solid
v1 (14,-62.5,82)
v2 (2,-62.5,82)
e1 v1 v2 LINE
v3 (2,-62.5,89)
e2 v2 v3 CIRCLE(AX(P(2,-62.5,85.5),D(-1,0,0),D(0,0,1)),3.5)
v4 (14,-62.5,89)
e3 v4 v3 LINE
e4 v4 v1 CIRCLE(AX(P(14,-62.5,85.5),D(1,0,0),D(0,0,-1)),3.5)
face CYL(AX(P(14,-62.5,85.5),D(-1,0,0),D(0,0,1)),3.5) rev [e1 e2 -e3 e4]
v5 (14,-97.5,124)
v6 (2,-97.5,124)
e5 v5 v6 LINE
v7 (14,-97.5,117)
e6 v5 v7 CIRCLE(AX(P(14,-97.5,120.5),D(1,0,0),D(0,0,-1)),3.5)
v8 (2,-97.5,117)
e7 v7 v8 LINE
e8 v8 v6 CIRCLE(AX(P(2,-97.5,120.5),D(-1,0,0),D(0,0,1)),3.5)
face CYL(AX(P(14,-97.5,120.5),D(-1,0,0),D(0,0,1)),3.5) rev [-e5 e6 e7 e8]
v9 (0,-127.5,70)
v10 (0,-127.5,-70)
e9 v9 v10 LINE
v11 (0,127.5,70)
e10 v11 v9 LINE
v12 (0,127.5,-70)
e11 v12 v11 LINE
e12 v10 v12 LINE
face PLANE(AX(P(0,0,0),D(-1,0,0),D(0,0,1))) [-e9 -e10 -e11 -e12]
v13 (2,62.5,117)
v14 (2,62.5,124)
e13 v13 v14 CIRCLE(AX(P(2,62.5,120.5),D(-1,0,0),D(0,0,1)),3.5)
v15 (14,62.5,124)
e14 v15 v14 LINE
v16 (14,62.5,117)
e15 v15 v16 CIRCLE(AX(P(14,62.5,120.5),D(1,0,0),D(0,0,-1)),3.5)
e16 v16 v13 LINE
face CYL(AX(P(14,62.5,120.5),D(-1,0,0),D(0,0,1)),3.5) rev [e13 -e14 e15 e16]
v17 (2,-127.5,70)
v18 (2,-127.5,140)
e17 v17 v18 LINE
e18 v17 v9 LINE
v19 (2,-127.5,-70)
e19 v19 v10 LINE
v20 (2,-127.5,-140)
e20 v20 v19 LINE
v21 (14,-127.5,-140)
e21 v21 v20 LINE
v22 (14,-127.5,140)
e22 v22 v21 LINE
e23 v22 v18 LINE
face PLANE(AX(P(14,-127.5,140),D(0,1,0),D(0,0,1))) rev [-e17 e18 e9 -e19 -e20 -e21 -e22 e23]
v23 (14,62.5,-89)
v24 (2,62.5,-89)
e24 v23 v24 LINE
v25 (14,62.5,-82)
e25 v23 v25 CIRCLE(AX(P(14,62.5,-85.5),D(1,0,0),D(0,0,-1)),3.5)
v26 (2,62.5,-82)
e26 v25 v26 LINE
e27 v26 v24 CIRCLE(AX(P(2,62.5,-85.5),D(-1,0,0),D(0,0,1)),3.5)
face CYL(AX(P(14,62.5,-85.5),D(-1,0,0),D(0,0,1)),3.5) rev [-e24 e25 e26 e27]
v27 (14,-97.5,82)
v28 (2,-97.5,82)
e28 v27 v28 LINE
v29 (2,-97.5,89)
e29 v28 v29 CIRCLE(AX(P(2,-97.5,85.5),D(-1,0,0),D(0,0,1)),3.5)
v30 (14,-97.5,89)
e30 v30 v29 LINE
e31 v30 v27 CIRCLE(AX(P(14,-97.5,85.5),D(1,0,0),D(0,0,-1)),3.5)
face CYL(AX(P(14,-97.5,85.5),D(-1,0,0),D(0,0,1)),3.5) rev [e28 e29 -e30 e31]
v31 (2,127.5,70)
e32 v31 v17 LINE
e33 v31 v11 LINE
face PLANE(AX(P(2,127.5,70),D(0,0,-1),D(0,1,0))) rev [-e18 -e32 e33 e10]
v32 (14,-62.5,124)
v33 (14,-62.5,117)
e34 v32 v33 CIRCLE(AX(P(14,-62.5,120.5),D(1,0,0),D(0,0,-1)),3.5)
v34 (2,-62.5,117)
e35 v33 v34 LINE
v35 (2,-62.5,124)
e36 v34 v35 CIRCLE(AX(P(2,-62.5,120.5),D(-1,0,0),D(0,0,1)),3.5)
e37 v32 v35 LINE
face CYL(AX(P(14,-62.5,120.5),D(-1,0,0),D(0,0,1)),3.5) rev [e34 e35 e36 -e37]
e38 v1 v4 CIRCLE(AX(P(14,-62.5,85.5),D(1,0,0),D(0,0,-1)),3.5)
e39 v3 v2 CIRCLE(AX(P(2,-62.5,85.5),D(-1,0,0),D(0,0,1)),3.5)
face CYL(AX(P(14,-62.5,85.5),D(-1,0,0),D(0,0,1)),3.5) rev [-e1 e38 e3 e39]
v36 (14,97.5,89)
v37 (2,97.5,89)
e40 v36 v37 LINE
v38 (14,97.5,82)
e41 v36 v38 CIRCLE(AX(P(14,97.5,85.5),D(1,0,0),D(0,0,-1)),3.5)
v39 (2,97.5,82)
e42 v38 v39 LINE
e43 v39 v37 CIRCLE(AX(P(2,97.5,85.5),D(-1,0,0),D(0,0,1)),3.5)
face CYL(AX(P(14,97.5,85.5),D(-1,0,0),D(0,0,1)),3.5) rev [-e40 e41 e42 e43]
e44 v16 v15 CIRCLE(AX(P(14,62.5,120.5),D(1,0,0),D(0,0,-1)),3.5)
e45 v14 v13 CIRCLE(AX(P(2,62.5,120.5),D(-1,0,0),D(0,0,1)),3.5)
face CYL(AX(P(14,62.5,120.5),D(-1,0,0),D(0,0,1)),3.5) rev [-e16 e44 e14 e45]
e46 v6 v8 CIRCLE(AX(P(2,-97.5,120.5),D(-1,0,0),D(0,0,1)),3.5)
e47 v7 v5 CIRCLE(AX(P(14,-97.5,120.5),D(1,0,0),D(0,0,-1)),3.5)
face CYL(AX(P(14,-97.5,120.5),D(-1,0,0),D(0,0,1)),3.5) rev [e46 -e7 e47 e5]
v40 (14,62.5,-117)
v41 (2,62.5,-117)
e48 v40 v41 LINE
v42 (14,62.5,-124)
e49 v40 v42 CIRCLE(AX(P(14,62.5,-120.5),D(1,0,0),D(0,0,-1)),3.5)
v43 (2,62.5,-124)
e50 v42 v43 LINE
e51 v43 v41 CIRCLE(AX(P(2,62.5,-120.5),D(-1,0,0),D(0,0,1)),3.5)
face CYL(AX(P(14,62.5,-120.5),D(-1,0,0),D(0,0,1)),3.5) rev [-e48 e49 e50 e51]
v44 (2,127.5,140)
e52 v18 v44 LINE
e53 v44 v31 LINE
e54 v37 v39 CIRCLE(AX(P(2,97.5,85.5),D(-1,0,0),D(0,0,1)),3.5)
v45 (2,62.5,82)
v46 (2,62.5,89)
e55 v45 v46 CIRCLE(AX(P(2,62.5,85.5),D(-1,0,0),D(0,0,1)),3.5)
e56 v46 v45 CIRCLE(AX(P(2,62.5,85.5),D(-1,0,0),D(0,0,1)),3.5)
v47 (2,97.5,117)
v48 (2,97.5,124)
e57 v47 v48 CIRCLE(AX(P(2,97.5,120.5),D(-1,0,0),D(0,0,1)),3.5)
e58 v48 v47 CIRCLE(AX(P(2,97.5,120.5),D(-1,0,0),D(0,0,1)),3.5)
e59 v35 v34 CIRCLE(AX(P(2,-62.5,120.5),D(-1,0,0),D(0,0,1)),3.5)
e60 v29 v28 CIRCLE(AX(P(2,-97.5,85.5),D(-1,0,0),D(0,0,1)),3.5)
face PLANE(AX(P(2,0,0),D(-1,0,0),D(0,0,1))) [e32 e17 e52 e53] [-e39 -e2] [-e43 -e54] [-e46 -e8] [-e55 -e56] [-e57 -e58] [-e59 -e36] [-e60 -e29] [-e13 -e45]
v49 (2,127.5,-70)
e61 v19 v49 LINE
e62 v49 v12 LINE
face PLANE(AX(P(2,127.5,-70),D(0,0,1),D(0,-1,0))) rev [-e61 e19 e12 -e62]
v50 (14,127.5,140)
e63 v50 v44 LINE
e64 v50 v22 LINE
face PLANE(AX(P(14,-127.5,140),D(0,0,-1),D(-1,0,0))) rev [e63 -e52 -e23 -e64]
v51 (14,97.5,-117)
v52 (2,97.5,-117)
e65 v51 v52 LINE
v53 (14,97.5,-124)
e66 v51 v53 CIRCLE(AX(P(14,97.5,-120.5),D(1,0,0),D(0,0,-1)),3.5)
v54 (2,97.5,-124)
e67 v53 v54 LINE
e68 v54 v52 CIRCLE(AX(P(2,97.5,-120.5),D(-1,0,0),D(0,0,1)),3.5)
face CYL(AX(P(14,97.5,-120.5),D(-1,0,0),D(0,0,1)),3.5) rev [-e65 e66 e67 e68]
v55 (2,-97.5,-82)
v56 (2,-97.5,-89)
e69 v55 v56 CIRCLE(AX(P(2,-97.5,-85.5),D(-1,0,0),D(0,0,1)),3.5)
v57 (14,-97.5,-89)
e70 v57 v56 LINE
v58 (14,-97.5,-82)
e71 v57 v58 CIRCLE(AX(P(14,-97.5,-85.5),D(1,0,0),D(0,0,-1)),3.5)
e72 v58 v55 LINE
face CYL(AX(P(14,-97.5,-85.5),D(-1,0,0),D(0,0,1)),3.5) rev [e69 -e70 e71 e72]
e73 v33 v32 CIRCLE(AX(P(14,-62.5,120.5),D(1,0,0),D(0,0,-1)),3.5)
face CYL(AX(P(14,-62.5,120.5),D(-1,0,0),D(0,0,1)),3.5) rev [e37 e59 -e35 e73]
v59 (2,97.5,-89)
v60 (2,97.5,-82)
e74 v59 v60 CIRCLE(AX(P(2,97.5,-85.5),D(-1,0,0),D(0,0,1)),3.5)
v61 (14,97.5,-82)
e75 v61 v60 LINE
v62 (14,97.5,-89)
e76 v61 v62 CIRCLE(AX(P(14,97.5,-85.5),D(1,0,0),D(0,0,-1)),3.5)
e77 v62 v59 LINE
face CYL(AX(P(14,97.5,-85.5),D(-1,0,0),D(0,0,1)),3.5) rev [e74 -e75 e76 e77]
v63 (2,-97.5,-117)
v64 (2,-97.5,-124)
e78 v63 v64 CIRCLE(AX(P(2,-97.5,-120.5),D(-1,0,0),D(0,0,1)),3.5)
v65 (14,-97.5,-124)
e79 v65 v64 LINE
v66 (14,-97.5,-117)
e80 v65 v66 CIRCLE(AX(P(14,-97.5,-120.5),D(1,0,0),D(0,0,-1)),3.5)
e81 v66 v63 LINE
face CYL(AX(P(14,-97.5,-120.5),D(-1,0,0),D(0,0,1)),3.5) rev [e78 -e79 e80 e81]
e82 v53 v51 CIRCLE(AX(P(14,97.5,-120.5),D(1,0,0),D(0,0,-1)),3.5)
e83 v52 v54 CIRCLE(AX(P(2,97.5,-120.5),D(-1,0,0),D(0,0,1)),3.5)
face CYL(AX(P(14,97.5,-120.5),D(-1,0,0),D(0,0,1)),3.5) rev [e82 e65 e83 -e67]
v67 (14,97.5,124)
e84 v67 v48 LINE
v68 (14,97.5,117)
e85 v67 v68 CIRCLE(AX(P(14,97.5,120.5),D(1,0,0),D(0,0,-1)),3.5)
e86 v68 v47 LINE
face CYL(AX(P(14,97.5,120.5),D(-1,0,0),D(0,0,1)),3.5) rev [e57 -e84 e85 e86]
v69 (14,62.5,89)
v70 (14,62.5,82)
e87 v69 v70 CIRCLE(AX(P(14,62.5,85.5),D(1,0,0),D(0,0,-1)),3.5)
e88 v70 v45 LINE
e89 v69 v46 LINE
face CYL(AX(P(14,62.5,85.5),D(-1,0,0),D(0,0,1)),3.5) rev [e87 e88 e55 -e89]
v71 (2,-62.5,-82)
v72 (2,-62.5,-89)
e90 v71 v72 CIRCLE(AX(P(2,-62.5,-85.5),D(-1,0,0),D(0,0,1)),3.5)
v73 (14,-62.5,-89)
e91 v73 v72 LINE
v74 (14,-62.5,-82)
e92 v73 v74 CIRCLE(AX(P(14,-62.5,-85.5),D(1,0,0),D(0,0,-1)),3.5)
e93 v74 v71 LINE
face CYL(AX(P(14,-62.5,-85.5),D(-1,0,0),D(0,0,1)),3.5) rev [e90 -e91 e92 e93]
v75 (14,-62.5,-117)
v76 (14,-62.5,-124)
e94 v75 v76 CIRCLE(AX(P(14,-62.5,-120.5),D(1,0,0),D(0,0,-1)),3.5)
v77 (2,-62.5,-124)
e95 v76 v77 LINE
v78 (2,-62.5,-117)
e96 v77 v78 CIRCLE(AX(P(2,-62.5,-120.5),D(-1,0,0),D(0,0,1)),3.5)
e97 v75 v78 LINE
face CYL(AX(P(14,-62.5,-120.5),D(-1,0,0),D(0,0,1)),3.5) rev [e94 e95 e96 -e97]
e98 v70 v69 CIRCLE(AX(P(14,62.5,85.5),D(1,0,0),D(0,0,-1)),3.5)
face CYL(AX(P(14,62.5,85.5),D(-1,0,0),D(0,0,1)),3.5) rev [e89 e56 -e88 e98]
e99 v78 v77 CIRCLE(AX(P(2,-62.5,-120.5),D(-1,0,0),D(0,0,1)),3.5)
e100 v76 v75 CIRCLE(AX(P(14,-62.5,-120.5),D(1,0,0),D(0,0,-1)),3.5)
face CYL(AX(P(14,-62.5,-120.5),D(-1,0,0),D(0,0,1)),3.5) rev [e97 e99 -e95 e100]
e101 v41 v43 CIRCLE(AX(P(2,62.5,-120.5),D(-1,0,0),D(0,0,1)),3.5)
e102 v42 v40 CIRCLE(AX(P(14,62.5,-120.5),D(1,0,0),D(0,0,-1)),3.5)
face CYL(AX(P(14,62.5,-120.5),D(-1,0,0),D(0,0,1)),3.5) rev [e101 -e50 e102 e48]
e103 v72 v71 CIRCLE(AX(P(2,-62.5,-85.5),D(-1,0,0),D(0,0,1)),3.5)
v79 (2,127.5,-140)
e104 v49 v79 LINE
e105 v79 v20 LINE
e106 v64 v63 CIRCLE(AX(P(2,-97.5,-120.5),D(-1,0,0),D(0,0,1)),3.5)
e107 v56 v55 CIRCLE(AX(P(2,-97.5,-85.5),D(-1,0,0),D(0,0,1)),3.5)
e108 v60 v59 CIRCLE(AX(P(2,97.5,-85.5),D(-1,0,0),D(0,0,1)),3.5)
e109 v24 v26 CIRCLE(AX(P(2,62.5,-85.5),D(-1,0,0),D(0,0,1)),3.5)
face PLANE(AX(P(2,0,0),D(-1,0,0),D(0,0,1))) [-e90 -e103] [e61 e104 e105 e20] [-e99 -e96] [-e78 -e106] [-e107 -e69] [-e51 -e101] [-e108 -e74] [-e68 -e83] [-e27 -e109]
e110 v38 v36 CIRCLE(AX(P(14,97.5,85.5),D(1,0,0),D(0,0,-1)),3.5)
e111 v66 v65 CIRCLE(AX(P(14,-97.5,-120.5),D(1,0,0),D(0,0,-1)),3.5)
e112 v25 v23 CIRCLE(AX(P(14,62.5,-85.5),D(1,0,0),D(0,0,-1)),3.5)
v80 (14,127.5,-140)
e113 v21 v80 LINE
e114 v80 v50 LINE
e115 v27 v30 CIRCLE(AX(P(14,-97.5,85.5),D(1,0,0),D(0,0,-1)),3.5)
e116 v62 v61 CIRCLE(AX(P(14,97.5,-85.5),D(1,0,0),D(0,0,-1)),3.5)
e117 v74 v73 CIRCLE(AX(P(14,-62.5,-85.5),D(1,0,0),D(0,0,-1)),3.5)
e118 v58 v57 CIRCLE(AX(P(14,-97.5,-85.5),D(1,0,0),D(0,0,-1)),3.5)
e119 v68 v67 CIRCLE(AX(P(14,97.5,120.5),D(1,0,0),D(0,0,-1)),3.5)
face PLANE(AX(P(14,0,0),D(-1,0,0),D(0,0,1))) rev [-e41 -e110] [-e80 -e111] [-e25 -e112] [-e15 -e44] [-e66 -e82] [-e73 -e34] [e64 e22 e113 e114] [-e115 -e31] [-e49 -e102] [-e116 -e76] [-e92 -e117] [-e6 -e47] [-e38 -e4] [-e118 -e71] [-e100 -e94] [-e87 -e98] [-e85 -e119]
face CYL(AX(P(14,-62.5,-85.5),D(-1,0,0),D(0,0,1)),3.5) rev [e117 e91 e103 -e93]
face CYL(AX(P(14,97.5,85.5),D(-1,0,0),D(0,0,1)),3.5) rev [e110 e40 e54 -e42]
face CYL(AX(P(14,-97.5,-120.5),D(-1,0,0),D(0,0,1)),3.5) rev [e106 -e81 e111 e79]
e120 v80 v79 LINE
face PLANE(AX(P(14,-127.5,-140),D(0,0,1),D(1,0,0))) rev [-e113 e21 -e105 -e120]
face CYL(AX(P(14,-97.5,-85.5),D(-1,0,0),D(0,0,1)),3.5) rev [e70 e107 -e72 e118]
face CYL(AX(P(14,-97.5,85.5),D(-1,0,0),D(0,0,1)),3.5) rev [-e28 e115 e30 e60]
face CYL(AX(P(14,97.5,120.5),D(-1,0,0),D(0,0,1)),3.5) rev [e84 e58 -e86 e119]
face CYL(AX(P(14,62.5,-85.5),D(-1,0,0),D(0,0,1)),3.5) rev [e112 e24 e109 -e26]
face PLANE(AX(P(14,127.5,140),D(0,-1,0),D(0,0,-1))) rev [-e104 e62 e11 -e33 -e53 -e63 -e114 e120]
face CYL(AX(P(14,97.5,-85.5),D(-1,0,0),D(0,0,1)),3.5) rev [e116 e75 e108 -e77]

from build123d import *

# Parameters (mm, degrees)
SKETCH1_W           = 280
SKETCH1_H           = 255
SKETCH1_R           = 3.5
BOSS_EXTRUDE1_DEPTH = 14
SKETCH6_W           = 70
SKETCH6_H           = 255
CUT_EXTRUDE3_DEPTH  = 2


with BuildPart() as part:
    # Sketch1 → Boss-Extrude1 (new body)
    with BuildSketch(Plane(origin=(0, 0, 0), x_dir=(0, 0, -1), z_dir=(1, 0, 0))):
        Rectangle(SKETCH1_W, SKETCH1_H)
        with Locations((-120.5, 97.5)):
            Circle(SKETCH1_R, mode=Mode.SUBTRACT)
        with Locations((-85.5, 97.5)):
            Circle(SKETCH1_R, mode=Mode.SUBTRACT)
        with Locations((-120.5, -97.5)):
            Circle(SKETCH1_R, mode=Mode.SUBTRACT)
        with Locations((-85.5, -97.5)):
            Circle(SKETCH1_R, mode=Mode.SUBTRACT)
        with Locations((-120.5, 62.5)):
            Circle(SKETCH1_R, mode=Mode.SUBTRACT)
        with Locations((-85.5, 62.5)):
            Circle(SKETCH1_R, mode=Mode.SUBTRACT)
        with Locations((-120.5, -62.5)):
            Circle(SKETCH1_R, mode=Mode.SUBTRACT)
        with Locations((-85.5, -62.5)):
            Circle(SKETCH1_R, mode=Mode.SUBTRACT)
        with Locations((85.5, 97.5)):
            Circle(SKETCH1_R, mode=Mode.SUBTRACT)
        with Locations((120.5, 97.5)):
            Circle(SKETCH1_R, mode=Mode.SUBTRACT)
        with Locations((85.5, -62.5)):
            Circle(SKETCH1_R, mode=Mode.SUBTRACT)
        with Locations((120.5, -62.5)):
            Circle(SKETCH1_R, mode=Mode.SUBTRACT)
        with Locations((85.5, -97.5)):
            Circle(SKETCH1_R, mode=Mode.SUBTRACT)
        with Locations((120.5, -97.5)):
            Circle(SKETCH1_R, mode=Mode.SUBTRACT)
        with Locations((85.5, 62.5)):
            Circle(SKETCH1_R, mode=Mode.SUBTRACT)
        with Locations((120.5, 62.5)):
            Circle(SKETCH1_R, mode=Mode.SUBTRACT)
    extrude(amount=BOSS_EXTRUDE1_DEPTH)

    # Sketch6 → Cut-Extrude3 (cut)
    with BuildSketch(Plane.ZY):
        with Locations((-105, 0)):
            Rectangle(SKETCH6_W, SKETCH6_H)
        with Locations((105, 0)):
            Rectangle(SKETCH6_W, SKETCH6_H)
    extrude(amount=-CUT_EXTRUDE3_DEPTH, mode=Mode.SUBTRACT)


solid = part.part
